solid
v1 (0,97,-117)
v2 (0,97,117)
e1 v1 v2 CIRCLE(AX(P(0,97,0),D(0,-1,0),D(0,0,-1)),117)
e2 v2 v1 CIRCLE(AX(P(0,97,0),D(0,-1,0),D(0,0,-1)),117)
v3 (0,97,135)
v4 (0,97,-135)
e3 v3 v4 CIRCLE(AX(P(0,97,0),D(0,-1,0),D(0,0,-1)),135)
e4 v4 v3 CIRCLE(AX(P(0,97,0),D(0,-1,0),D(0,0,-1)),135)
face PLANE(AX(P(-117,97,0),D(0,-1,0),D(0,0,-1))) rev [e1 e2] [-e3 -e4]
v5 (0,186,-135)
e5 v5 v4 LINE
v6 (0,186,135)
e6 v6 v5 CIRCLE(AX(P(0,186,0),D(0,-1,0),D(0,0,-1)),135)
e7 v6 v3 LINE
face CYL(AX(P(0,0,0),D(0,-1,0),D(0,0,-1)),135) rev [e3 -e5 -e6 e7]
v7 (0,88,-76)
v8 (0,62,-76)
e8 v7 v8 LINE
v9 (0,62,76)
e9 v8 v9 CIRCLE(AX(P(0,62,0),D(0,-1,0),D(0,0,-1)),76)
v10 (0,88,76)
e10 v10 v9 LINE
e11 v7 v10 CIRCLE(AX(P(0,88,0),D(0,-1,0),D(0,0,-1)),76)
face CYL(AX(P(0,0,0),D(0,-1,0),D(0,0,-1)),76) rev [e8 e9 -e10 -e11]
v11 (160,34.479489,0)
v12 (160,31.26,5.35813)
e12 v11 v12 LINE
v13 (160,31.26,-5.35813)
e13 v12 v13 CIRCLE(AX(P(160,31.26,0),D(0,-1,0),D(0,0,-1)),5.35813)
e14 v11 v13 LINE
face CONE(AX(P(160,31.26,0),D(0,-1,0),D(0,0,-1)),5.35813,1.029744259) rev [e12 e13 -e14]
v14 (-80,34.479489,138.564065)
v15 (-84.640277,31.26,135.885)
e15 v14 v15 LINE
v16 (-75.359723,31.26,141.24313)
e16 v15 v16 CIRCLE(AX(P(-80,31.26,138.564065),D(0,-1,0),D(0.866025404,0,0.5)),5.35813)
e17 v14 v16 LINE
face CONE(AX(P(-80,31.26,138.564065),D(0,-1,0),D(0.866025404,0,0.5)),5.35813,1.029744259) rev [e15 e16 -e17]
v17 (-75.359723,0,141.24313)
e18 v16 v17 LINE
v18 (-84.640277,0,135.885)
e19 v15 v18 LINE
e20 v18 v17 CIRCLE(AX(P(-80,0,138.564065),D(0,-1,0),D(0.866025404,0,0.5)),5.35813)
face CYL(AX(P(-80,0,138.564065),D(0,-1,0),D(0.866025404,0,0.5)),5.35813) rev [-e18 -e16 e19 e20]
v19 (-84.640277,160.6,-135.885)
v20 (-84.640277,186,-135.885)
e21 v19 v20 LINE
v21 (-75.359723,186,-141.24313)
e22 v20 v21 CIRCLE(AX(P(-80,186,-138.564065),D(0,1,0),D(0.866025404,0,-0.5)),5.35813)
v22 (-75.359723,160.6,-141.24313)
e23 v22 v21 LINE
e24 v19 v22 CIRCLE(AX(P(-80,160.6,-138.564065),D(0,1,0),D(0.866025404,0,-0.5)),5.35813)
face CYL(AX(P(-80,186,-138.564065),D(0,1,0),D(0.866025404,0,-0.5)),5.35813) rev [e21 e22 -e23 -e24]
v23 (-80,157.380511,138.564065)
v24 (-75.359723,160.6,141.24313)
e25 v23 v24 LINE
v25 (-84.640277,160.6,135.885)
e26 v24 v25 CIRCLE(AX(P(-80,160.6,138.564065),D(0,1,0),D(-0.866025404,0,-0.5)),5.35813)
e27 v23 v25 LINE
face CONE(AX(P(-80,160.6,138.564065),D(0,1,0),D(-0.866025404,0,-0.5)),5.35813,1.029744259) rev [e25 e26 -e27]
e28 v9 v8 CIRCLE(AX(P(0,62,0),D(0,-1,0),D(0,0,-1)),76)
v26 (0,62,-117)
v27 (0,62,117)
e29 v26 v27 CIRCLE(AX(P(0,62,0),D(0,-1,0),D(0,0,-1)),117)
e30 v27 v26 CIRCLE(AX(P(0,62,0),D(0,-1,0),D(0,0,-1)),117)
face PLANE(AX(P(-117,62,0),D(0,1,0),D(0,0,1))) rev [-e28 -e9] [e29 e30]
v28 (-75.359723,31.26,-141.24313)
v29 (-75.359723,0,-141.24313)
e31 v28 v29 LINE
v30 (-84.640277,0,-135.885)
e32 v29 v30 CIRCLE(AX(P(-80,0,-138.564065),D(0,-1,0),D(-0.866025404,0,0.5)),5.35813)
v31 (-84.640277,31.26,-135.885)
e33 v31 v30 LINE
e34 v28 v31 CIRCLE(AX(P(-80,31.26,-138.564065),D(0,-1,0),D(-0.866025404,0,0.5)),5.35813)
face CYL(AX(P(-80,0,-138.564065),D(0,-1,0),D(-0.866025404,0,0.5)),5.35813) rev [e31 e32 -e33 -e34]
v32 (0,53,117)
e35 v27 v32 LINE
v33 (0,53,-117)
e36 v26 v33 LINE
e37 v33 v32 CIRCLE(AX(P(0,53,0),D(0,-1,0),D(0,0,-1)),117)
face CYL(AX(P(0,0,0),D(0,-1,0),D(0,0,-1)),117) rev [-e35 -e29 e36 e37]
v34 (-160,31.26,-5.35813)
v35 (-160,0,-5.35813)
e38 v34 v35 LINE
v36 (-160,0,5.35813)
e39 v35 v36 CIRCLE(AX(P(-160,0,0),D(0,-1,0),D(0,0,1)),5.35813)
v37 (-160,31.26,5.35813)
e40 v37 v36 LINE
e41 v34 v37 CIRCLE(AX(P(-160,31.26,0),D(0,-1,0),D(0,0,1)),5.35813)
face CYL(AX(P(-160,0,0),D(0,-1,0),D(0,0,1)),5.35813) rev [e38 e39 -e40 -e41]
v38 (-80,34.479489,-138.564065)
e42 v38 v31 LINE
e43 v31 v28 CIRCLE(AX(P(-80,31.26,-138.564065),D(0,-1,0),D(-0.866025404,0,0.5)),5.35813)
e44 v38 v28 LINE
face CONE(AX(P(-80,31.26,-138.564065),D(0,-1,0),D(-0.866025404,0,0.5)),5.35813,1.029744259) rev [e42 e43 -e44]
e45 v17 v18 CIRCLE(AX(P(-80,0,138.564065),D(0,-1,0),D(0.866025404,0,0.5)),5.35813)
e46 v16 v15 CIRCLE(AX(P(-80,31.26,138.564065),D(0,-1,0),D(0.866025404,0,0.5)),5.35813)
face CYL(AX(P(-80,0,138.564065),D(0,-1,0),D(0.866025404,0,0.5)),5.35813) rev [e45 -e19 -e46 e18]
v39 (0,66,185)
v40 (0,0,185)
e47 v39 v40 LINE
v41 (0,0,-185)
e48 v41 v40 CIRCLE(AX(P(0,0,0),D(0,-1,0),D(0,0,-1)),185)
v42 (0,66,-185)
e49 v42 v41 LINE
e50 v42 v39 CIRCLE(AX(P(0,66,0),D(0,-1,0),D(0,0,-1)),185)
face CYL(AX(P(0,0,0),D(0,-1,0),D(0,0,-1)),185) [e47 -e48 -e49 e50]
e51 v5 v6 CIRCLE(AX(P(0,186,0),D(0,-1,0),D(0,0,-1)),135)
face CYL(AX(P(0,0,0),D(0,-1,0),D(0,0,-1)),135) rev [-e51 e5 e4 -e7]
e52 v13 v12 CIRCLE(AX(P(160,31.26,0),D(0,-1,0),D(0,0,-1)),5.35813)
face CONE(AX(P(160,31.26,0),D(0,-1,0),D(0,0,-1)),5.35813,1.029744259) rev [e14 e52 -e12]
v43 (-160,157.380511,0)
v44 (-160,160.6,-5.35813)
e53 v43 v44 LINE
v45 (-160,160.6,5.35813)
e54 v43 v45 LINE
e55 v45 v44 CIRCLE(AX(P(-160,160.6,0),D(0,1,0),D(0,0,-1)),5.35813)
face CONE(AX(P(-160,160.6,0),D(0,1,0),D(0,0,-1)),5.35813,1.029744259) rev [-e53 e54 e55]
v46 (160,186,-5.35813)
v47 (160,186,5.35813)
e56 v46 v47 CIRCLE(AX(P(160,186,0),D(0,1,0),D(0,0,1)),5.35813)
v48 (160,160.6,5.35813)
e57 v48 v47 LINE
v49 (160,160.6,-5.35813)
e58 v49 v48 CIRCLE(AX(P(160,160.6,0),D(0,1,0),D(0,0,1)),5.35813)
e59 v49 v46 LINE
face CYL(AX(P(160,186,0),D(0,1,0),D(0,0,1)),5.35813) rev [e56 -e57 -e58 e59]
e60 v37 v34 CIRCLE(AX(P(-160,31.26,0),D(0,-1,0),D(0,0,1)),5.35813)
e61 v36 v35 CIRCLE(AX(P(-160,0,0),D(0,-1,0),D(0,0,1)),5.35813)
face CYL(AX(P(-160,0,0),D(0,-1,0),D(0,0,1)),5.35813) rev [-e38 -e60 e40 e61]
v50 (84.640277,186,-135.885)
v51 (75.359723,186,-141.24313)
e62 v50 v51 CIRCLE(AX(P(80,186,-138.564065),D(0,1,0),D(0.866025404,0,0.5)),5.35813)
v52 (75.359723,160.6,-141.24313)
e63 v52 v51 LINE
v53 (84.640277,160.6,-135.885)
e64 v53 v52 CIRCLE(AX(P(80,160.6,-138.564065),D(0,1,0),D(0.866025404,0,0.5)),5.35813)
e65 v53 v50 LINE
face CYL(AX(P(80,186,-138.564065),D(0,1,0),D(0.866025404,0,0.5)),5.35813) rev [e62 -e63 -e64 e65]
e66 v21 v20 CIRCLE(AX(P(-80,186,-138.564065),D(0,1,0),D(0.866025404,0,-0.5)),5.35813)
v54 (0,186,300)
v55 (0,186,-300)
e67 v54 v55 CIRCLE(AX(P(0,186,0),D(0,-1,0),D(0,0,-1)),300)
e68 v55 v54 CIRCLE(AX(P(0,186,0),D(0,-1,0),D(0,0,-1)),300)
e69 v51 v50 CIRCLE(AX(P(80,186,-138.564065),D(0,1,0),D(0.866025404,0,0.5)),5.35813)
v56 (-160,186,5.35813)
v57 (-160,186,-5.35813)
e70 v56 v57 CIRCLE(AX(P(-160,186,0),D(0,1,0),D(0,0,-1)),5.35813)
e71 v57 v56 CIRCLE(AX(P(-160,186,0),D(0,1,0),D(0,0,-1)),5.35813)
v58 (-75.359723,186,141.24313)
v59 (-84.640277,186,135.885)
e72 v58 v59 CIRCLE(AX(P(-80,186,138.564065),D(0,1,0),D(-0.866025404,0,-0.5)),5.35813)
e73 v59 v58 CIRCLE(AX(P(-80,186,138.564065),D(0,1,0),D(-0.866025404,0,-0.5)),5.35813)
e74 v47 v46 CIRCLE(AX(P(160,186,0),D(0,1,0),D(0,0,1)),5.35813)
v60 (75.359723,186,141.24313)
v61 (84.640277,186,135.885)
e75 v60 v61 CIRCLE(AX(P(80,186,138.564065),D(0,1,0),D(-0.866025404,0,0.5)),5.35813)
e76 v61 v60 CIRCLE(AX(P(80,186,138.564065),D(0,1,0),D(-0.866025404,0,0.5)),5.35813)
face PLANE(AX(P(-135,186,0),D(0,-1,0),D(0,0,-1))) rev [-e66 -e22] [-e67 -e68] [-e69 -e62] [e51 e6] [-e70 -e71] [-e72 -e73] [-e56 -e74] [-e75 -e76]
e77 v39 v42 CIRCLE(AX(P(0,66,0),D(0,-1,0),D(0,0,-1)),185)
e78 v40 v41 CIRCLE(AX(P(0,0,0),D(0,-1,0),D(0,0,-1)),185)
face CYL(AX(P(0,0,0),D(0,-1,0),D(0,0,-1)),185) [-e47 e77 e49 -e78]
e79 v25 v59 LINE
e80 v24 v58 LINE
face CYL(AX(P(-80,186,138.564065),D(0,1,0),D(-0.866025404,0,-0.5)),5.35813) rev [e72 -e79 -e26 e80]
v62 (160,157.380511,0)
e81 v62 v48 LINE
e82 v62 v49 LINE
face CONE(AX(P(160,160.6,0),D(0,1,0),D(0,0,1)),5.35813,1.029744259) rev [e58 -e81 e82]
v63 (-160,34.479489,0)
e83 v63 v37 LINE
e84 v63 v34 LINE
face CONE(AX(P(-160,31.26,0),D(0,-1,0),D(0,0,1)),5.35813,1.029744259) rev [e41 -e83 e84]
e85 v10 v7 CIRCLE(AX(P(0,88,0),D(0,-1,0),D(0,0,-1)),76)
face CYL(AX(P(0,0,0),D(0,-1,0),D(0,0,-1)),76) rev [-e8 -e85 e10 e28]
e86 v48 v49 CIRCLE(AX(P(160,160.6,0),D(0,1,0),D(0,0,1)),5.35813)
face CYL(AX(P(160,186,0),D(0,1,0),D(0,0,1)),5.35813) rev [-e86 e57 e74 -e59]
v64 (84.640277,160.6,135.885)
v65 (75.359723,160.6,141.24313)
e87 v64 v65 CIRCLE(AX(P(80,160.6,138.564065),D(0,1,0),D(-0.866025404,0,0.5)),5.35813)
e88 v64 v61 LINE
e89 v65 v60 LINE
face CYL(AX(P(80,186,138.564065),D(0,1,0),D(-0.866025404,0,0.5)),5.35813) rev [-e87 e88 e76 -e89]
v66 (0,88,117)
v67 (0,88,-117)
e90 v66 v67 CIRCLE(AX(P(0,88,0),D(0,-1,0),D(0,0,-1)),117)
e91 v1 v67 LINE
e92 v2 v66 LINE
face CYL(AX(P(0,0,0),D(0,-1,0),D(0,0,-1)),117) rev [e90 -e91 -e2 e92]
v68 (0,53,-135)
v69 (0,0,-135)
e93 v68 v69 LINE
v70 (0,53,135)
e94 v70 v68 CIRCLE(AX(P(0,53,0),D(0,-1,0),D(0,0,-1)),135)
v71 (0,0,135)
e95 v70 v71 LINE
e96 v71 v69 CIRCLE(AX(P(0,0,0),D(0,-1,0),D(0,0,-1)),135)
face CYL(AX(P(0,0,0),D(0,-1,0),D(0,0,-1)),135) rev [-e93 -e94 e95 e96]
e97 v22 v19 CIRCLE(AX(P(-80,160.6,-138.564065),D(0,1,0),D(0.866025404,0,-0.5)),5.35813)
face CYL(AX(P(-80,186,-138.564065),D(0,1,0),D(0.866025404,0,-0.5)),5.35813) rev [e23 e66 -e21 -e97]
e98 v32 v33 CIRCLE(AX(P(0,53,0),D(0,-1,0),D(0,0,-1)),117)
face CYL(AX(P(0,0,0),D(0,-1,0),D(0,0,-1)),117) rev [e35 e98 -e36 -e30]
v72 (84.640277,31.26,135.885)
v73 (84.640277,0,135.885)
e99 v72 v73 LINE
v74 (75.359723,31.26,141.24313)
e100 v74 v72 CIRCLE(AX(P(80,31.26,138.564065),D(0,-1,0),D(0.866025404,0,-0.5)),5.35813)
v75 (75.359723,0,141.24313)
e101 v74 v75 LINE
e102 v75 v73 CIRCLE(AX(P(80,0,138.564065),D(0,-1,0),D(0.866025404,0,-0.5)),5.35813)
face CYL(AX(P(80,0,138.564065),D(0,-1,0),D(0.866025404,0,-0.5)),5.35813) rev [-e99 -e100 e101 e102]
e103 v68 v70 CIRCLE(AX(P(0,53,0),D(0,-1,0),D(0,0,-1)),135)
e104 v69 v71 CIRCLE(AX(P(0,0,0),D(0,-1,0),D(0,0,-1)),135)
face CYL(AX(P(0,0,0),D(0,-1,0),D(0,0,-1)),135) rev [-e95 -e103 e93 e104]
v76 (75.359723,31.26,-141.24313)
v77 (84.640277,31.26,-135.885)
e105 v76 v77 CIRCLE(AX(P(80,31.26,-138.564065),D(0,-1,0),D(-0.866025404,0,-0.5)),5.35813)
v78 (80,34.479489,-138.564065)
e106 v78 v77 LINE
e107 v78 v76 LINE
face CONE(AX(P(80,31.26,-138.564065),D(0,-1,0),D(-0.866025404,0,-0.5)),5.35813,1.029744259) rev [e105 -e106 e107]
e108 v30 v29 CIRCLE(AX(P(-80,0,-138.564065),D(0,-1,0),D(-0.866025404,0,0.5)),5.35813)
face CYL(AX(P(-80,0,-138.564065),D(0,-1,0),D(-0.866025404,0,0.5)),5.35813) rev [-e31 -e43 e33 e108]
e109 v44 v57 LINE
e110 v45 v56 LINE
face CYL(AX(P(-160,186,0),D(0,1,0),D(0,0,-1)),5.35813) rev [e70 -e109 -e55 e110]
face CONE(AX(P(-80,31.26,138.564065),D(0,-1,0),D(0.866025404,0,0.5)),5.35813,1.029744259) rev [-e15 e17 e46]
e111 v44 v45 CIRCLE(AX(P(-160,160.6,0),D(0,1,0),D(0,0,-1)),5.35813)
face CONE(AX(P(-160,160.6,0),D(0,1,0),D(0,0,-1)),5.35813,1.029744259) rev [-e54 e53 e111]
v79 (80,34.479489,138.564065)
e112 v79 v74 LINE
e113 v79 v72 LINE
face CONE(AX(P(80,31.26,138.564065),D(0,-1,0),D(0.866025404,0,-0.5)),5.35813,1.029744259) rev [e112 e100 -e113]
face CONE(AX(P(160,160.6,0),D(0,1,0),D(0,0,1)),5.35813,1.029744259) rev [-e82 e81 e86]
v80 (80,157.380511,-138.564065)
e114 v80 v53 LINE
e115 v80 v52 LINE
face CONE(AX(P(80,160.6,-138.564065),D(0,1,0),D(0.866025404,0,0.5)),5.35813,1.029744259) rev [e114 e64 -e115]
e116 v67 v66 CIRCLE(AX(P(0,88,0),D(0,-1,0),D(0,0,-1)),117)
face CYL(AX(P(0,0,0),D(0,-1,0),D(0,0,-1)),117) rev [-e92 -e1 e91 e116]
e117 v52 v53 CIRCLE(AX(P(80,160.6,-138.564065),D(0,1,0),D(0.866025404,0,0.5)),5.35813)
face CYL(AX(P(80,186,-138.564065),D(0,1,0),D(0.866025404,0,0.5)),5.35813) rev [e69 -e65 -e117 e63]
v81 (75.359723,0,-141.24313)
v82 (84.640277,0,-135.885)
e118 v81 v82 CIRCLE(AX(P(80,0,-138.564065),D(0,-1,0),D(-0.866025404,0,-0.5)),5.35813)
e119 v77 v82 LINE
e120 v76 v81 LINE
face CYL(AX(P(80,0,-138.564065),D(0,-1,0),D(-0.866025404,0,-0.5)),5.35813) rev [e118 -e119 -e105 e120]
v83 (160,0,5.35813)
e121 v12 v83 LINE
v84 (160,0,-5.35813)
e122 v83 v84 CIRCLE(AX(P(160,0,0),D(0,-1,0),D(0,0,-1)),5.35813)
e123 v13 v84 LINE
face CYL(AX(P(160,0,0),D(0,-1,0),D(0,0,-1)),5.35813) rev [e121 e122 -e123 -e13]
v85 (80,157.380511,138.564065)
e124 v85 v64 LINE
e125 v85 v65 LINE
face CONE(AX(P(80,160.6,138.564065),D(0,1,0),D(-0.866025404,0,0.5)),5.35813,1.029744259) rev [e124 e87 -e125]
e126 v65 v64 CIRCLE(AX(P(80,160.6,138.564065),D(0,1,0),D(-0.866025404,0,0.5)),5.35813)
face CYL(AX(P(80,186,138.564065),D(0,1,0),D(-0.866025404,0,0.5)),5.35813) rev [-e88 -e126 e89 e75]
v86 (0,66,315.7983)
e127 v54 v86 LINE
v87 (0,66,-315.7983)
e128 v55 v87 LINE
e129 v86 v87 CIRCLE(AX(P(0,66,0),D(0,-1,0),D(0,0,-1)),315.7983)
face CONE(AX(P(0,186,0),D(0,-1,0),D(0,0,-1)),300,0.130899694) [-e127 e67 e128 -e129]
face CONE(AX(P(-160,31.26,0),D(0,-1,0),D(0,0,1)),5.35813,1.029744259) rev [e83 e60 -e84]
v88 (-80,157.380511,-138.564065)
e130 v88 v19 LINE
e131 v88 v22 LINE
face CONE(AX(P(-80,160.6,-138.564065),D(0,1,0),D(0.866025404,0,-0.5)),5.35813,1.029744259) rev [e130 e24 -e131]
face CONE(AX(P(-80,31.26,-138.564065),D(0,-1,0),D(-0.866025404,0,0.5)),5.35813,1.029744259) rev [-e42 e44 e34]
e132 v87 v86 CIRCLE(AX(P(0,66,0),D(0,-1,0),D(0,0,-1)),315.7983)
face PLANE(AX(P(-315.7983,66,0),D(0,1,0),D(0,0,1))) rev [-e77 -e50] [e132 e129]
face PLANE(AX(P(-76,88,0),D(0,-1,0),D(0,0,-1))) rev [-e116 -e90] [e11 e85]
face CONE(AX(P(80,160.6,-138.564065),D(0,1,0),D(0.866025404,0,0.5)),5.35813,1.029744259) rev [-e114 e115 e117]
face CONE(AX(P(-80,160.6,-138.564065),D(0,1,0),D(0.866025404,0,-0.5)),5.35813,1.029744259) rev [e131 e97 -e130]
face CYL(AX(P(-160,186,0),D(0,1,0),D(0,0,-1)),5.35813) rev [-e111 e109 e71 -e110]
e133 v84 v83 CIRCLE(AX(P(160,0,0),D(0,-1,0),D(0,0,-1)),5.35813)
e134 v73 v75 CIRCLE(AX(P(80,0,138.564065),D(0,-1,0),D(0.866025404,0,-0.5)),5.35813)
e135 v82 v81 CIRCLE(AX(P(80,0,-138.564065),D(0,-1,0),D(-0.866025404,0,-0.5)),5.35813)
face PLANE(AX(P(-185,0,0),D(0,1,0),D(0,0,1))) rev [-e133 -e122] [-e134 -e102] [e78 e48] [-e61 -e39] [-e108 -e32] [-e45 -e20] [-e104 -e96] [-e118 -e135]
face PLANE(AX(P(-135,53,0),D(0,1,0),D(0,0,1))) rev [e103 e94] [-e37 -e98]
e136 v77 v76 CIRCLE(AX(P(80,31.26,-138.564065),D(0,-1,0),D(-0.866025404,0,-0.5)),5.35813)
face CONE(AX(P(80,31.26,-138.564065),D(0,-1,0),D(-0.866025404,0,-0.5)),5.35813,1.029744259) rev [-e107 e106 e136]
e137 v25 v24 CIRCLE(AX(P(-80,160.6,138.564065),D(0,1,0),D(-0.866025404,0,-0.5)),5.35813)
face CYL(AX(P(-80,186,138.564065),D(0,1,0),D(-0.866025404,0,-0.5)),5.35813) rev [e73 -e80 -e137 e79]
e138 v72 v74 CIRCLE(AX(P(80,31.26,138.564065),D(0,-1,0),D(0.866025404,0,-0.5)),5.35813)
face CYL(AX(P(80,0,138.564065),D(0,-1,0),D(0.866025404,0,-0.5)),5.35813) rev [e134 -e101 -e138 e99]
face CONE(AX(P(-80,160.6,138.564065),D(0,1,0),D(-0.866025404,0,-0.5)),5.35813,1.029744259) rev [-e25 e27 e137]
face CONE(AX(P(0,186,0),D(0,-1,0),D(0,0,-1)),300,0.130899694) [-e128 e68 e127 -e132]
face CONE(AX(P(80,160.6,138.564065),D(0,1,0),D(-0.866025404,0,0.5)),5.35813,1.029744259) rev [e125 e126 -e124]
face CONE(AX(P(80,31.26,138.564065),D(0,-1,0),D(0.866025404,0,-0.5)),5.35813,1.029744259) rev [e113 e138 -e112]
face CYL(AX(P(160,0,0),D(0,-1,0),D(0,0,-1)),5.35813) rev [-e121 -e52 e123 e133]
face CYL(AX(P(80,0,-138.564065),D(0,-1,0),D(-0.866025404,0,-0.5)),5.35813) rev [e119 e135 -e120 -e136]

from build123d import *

# Parameters (mm, degrees)
CIRPATTERN1_COUNT = 6
CIRPATTERN2_COUNT = 6


with BuildPart() as part:
    # Sketch1 → Revolve1 (revolve)
    with BuildSketch(Plane.XY, mode=Mode.PRIVATE) as revolve1_sk:
        Polygon((-135, 0), (-135, 53), (-117, 53), (-117, 62), (-76, 62), (-76, 88), (-117, 88), (-117, 97), (-135, 97), (-135, 186), (-300, 186), (-315.79829971, 66), (-185, 66), (-185, 0), align=None)
    revolve(revolve1_sk.sketch.rotate(Axis((0, 0, 0), (0, 1, 0)), 270), axis=Axis((0, 0, 0), (0, 1, 0)))

    # Sketch3 → 1/2-13 Tapped Hole1 (revolve, cut)
    with BuildSketch(Plane(origin=(160, 186, 0), x_dir=(0, 0, 1), z_dir=(1, 0, 0))):
        Polygon((0, 0), (0, 28.619489309), (5.35813, 25.4), (5.35813, 0), align=None)
    f_1_2_13_tapped_hole1 = revolve(axis=Axis((160, 192.35, 0), (0, -1, 0)), mode=Mode.SUBTRACT)

    # CirPattern1: 1/2-13 Tapped Hole1 ×6 about axis
    cirpattern1_axis = Axis((0, 0, 0), (0, 1, 0))
    for i in range(1, CIRPATTERN1_COUNT):
        add(f_1_2_13_tapped_hole1.rotate(cirpattern1_axis, i * 360 / CIRPATTERN1_COUNT), mode=Mode.SUBTRACT)

    # Sketch5 → 1/2-13 Tapped Hole2 (revolve, cut)
    with BuildSketch(Plane(origin=(160, 0, 0), x_dir=(0, 0, -1), z_dir=(1, 0, 0))):
        Polygon((0, 0), (0, 34.479489309), (5.35813, 31.26), (5.35813, 0), align=None)
    f_1_2_13_tapped_hole2 = revolve(axis=Axis((160, -6.35, 0), (0, 1, 0)), mode=Mode.SUBTRACT)

    # CirPattern2: 1/2-13 Tapped Hole2 ×6 about axis
    cirpattern2_axis = Axis((0, 0, 0), (0, 1, 0))
    for i in range(1, CIRPATTERN2_COUNT):
        add(f_1_2_13_tapped_hole2.rotate(cirpattern2_axis, i * 360 / CIRPATTERN2_COUNT), mode=Mode.SUBTRACT)


solid = part.part
